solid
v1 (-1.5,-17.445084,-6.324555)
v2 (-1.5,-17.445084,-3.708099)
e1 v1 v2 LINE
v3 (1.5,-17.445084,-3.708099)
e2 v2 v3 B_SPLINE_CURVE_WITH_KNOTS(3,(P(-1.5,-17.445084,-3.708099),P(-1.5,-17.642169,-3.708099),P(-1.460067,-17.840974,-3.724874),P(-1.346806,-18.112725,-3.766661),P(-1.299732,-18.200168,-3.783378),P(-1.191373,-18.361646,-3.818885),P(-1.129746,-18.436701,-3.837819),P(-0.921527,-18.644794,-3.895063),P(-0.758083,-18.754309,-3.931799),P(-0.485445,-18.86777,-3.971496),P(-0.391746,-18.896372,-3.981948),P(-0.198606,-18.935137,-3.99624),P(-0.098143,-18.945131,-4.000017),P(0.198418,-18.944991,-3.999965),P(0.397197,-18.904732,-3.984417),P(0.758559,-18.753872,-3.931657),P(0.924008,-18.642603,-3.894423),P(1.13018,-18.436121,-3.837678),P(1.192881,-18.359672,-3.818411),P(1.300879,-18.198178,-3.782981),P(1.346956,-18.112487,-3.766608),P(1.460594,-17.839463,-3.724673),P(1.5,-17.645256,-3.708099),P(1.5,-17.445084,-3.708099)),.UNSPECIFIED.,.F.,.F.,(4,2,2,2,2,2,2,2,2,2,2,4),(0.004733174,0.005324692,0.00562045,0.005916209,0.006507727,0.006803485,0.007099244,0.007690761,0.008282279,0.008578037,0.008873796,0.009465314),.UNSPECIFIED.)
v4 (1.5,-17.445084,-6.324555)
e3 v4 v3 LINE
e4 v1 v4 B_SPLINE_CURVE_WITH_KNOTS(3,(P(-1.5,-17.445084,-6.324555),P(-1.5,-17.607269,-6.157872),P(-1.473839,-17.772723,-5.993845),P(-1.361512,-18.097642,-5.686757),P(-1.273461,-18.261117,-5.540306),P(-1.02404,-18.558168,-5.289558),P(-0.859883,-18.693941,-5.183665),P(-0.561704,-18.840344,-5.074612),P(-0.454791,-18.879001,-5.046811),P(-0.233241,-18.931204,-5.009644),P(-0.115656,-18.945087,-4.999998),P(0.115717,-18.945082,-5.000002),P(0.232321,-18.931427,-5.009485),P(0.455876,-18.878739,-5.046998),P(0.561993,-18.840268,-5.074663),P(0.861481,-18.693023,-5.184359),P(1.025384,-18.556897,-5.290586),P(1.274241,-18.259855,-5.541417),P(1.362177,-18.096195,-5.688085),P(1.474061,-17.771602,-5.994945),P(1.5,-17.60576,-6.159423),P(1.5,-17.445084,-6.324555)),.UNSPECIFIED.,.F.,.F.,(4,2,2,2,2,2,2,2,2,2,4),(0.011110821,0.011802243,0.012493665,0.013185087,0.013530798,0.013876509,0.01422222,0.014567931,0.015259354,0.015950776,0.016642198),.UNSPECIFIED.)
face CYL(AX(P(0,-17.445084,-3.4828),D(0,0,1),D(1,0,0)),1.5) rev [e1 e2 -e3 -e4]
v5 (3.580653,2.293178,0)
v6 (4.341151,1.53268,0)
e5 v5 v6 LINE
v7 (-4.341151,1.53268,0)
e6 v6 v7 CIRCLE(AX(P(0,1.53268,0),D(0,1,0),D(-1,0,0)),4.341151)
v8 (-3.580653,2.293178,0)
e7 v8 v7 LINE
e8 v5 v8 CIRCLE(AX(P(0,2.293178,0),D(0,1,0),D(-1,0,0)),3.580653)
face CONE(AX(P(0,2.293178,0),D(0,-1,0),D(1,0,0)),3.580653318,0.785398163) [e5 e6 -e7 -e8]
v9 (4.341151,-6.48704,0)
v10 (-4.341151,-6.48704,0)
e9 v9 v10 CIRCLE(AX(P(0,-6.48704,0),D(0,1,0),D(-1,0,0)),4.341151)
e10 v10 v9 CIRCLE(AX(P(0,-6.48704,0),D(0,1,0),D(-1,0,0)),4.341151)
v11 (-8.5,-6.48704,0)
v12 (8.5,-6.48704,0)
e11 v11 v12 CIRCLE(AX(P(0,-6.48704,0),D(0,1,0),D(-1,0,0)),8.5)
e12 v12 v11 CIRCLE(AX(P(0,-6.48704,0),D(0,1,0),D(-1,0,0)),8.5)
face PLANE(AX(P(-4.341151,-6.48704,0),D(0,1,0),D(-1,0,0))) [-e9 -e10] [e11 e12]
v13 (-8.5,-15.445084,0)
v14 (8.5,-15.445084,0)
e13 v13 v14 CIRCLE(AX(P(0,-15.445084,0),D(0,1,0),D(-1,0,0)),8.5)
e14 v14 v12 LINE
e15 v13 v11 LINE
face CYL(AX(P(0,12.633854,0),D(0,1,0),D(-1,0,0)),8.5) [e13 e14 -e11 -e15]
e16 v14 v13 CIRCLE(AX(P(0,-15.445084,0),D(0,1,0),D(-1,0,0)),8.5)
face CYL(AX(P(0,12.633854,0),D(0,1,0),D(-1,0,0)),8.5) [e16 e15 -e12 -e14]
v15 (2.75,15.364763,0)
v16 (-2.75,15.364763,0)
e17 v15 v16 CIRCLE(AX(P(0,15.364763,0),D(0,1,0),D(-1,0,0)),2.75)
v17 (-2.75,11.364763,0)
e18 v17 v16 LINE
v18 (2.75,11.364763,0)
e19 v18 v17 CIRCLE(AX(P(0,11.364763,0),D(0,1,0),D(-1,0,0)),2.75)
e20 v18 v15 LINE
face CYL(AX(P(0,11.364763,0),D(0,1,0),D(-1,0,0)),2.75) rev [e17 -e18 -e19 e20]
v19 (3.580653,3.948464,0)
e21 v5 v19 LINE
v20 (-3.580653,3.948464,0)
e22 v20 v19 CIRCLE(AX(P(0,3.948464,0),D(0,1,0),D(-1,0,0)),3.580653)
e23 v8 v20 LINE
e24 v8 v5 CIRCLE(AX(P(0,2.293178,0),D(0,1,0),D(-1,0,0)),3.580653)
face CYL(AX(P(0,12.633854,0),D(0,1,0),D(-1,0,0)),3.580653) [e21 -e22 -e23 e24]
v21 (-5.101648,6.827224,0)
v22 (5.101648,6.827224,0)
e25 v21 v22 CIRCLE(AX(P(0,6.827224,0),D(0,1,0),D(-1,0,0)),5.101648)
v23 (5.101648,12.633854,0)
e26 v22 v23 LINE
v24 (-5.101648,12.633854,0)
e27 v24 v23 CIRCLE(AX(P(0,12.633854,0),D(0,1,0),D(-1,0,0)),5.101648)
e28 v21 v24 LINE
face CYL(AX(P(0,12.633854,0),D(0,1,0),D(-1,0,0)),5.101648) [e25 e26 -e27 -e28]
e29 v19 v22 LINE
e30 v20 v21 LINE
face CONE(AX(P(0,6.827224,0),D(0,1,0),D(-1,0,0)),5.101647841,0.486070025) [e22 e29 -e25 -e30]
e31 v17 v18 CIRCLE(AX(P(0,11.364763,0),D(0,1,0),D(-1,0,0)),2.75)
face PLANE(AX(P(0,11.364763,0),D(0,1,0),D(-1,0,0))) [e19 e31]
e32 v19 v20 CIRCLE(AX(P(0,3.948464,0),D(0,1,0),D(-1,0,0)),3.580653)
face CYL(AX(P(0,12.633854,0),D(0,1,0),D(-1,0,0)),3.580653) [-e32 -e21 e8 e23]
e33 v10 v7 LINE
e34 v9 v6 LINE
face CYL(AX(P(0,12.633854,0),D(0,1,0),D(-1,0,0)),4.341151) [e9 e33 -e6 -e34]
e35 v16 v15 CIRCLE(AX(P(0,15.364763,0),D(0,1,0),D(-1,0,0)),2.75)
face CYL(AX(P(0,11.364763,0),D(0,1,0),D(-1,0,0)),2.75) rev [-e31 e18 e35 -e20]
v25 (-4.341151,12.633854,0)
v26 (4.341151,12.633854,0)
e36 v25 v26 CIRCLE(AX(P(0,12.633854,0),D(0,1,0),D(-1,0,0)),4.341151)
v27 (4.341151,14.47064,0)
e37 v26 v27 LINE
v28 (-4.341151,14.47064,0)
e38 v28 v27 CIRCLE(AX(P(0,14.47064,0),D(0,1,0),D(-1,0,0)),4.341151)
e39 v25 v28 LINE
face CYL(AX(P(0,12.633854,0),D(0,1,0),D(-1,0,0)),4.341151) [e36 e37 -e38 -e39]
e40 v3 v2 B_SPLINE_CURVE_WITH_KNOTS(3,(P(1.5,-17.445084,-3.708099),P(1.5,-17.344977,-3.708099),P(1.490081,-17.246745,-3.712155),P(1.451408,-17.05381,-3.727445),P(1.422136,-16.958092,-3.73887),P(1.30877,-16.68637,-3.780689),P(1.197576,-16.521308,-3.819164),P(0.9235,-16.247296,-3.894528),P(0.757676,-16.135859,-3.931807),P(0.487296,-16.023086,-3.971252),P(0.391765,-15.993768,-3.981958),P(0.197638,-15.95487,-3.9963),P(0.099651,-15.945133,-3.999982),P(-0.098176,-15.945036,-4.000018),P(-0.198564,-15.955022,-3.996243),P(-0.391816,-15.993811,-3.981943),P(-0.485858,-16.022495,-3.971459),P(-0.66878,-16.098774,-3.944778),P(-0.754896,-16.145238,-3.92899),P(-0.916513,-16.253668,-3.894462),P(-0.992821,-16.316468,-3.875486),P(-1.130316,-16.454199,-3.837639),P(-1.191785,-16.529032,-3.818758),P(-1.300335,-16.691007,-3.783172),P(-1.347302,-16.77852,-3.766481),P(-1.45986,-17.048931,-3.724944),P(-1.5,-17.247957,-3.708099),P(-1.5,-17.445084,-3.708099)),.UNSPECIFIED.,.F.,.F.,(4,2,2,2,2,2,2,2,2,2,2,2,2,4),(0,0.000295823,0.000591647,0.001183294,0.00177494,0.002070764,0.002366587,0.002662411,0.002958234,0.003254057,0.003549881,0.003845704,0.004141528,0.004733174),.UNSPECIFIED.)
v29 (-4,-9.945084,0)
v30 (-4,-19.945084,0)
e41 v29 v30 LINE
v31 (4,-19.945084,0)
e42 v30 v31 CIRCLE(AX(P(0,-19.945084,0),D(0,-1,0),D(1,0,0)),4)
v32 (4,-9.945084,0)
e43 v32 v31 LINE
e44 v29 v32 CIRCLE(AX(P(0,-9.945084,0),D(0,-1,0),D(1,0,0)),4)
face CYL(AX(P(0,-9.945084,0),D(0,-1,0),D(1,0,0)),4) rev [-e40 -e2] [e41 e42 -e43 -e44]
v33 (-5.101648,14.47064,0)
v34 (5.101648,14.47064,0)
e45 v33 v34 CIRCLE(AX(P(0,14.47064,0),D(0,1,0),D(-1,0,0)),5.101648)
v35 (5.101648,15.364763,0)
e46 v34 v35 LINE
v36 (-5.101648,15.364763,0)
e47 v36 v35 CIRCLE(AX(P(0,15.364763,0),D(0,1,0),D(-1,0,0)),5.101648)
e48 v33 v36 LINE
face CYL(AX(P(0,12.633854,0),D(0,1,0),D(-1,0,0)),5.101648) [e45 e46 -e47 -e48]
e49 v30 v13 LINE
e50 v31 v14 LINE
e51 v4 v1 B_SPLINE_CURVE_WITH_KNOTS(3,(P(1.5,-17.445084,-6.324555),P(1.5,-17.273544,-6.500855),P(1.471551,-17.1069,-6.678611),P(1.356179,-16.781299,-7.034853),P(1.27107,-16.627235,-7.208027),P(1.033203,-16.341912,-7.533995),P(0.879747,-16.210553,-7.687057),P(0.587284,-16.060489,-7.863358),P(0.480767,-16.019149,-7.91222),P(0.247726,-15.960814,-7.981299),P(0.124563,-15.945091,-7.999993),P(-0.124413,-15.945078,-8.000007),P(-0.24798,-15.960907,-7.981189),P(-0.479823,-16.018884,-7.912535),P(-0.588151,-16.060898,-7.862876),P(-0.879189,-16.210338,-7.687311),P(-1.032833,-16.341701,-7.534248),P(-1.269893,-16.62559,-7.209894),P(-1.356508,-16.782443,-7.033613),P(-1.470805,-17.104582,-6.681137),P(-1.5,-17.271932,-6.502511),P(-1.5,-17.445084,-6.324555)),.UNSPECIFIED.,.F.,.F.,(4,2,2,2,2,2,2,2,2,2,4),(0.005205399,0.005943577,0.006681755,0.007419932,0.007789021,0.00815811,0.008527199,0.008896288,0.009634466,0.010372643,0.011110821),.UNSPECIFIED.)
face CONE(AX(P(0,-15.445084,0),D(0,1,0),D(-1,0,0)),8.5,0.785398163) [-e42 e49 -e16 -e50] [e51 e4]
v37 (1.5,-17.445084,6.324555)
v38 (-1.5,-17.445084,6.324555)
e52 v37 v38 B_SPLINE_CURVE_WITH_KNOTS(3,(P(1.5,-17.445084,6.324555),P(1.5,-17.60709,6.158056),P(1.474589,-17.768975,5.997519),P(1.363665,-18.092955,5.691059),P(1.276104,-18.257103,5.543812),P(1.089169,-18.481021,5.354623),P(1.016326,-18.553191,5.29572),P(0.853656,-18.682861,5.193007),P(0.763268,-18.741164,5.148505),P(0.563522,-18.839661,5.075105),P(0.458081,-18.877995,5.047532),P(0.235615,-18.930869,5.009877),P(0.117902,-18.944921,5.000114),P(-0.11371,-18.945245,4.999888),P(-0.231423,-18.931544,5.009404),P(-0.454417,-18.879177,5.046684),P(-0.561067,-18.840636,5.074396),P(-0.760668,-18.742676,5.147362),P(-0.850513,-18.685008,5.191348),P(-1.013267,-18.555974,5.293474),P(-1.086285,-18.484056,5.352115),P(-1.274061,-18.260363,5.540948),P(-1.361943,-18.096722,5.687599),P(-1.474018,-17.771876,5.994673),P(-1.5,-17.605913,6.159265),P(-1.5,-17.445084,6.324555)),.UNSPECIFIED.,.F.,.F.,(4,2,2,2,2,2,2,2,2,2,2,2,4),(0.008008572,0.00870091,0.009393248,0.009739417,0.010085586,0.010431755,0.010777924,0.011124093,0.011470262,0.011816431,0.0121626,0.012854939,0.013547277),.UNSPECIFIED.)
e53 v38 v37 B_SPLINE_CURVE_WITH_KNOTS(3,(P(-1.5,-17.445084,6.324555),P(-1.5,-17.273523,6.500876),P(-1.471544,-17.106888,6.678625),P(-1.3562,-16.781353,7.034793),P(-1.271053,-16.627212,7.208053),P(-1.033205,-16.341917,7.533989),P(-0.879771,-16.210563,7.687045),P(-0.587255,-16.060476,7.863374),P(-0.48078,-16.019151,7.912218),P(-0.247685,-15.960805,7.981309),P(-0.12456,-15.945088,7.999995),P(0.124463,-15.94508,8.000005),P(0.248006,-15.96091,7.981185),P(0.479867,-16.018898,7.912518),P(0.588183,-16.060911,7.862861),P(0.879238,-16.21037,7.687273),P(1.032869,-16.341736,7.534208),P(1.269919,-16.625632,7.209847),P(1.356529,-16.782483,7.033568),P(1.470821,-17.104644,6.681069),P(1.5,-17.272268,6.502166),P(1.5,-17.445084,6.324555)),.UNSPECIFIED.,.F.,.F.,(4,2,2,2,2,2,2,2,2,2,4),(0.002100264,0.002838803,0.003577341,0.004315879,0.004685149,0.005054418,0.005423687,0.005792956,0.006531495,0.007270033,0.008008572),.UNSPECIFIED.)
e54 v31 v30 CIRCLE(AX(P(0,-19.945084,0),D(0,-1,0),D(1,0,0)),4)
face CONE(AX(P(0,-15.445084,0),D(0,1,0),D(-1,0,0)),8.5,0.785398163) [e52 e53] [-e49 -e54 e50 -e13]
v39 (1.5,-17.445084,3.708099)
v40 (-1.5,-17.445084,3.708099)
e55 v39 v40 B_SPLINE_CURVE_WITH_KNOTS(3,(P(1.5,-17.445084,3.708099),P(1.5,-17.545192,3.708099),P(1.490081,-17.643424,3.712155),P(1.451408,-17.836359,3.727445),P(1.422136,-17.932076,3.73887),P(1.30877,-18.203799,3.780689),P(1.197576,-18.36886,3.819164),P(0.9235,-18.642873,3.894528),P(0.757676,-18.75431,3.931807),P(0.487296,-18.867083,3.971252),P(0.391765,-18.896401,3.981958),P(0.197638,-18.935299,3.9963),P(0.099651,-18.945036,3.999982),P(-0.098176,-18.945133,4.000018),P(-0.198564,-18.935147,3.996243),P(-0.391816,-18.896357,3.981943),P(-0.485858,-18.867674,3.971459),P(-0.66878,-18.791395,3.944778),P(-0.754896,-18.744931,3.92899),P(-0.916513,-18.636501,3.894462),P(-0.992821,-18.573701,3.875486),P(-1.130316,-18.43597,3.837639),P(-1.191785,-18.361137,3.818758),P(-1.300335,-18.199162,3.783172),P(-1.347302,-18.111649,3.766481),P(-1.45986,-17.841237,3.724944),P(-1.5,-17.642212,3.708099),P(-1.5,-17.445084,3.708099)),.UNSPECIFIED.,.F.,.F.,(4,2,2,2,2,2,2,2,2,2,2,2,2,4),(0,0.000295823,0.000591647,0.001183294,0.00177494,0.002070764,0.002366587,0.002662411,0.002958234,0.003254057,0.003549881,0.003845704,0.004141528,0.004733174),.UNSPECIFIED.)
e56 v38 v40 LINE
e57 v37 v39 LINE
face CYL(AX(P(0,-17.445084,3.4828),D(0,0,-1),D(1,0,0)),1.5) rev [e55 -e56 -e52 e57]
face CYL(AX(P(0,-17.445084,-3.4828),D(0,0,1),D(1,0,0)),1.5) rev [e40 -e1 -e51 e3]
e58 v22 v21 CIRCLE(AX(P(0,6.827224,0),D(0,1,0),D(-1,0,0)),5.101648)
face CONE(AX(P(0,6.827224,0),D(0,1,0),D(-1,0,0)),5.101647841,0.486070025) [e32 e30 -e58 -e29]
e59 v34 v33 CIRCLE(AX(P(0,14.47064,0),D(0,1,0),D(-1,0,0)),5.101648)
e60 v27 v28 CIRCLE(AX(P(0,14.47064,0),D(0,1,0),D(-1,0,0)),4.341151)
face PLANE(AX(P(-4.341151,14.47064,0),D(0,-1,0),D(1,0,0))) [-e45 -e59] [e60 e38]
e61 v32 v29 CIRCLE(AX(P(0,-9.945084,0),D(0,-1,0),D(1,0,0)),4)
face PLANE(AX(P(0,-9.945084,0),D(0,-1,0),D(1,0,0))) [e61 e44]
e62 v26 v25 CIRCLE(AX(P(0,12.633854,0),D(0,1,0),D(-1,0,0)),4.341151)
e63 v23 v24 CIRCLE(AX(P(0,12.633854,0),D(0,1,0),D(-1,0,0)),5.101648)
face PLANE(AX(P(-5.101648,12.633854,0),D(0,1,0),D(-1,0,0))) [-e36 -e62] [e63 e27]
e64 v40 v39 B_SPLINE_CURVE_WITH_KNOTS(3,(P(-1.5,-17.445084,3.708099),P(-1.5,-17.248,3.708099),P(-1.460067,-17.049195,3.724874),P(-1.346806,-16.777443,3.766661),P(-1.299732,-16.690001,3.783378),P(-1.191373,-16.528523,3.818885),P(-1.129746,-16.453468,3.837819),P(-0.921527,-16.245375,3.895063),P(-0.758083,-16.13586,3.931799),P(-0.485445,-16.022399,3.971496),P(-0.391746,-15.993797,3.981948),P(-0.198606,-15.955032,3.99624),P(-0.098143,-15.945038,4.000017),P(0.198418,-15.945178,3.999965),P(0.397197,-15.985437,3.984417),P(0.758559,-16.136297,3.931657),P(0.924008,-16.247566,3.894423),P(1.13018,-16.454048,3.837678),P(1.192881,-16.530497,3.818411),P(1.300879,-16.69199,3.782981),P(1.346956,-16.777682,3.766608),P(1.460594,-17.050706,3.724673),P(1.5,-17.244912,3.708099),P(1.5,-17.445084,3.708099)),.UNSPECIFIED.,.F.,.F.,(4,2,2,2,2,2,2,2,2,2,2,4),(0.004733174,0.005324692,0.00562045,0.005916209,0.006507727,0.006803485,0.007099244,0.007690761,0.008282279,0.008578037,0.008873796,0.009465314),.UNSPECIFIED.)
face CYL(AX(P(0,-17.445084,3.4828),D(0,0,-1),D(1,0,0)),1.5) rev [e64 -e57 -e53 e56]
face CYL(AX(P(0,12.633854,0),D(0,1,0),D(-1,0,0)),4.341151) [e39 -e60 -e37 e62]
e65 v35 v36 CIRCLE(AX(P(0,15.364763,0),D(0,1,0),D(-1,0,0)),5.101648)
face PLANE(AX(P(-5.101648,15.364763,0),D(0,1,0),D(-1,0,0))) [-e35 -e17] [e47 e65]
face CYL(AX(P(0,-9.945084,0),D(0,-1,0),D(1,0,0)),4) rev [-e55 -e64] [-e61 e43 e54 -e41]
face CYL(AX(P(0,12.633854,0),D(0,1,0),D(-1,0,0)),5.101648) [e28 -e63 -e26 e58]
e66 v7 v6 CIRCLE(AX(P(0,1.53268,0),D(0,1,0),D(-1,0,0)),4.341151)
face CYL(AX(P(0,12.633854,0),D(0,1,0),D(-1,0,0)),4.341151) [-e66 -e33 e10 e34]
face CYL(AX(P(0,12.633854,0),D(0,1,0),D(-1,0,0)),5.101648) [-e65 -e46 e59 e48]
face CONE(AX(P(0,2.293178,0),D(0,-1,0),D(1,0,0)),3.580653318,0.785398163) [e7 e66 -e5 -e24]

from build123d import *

# Parameters (mm, degrees)
SKETCH3_R          = 2.75
CUT_EXTRUDE2_DEPTH = 4
SKETCH4_R          = 4
CUT_EXTRUDE3_DEPTH = 10
SKETCH5_W          = 5.699016122
SKETCH5_H          = 1.5


with BuildPart() as part:
    # Sketch1 → Revolve1 (revolve)
    with BuildSketch(Plane.XY):
        Polygon((-8.5, -6.487039895), (-8.5, -15.445084434), (-4, -19.945084434), (0, -19.945084434), (0, 12.633854157), (0, 15.364763468), (-5.101647841, 15.364763468), (-5.101647841, 14.4706398), (-4.341150579, 14.4706398), (-4.341150579, 12.633854157), (-5.101647841, 12.633854157), (-5.101647841, 6.827224241), (-3.580653318, 3.948464428), (-3.580653318, 2.293177536), (-4.341150579, 1.532680274), (-4.341150579, -6.487039895), align=None)
    revolve(axis=Axis((0, 12.633854157, 0), (0, -1, 0)))

    # Sketch3 → Cut-Extrude2 (cut)
    with BuildSketch(Plane(origin=(0, 15.364763468, 0), x_dir=(1, 0, 0), z_dir=(0, 1, 0))):
        with Locations(Location((0, 0, 0), (0, 0, 180))):
            Circle(SKETCH3_R)
    extrude(amount=-CUT_EXTRUDE2_DEPTH, mode=Mode.SUBTRACT)

    # Sketch4 → Cut-Extrude3 (cut)
    with BuildSketch(Plane.XZ.offset(19.945084434)):
        Circle(SKETCH4_R)
    extrude(amount=-CUT_EXTRUDE3_DEPTH, mode=Mode.SUBTRACT)

    # Sketch5 → Cut-Revolve1 (revolve, cut)
    with BuildSketch(Plane(origin=(0, 0, 0), x_dir=(0, 0, -1), z_dir=(1, 0, 0)), mode=Mode.PRIVATE) as cut_revolve1_sk:
        with Locations((6.332308204, -16.695084434)):
            Rectangle(SKETCH5_W, SKETCH5_H)
    cut_revolve1 = revolve(cut_revolve1_sk.sketch.rotate(Axis((0, -17.445084434, -3.482800143), (0, 0, -1)), 90), axis=Axis((0, -17.445084434, -3.482800143), (0, 0, -1)), mode=Mode.SUBTRACT)

    # Mirror1: Cut-Revolve1 across plane
    add(cut_revolve1.mirror(Plane.XY), mode=Mode.SUBTRACT)


solid = part.part
